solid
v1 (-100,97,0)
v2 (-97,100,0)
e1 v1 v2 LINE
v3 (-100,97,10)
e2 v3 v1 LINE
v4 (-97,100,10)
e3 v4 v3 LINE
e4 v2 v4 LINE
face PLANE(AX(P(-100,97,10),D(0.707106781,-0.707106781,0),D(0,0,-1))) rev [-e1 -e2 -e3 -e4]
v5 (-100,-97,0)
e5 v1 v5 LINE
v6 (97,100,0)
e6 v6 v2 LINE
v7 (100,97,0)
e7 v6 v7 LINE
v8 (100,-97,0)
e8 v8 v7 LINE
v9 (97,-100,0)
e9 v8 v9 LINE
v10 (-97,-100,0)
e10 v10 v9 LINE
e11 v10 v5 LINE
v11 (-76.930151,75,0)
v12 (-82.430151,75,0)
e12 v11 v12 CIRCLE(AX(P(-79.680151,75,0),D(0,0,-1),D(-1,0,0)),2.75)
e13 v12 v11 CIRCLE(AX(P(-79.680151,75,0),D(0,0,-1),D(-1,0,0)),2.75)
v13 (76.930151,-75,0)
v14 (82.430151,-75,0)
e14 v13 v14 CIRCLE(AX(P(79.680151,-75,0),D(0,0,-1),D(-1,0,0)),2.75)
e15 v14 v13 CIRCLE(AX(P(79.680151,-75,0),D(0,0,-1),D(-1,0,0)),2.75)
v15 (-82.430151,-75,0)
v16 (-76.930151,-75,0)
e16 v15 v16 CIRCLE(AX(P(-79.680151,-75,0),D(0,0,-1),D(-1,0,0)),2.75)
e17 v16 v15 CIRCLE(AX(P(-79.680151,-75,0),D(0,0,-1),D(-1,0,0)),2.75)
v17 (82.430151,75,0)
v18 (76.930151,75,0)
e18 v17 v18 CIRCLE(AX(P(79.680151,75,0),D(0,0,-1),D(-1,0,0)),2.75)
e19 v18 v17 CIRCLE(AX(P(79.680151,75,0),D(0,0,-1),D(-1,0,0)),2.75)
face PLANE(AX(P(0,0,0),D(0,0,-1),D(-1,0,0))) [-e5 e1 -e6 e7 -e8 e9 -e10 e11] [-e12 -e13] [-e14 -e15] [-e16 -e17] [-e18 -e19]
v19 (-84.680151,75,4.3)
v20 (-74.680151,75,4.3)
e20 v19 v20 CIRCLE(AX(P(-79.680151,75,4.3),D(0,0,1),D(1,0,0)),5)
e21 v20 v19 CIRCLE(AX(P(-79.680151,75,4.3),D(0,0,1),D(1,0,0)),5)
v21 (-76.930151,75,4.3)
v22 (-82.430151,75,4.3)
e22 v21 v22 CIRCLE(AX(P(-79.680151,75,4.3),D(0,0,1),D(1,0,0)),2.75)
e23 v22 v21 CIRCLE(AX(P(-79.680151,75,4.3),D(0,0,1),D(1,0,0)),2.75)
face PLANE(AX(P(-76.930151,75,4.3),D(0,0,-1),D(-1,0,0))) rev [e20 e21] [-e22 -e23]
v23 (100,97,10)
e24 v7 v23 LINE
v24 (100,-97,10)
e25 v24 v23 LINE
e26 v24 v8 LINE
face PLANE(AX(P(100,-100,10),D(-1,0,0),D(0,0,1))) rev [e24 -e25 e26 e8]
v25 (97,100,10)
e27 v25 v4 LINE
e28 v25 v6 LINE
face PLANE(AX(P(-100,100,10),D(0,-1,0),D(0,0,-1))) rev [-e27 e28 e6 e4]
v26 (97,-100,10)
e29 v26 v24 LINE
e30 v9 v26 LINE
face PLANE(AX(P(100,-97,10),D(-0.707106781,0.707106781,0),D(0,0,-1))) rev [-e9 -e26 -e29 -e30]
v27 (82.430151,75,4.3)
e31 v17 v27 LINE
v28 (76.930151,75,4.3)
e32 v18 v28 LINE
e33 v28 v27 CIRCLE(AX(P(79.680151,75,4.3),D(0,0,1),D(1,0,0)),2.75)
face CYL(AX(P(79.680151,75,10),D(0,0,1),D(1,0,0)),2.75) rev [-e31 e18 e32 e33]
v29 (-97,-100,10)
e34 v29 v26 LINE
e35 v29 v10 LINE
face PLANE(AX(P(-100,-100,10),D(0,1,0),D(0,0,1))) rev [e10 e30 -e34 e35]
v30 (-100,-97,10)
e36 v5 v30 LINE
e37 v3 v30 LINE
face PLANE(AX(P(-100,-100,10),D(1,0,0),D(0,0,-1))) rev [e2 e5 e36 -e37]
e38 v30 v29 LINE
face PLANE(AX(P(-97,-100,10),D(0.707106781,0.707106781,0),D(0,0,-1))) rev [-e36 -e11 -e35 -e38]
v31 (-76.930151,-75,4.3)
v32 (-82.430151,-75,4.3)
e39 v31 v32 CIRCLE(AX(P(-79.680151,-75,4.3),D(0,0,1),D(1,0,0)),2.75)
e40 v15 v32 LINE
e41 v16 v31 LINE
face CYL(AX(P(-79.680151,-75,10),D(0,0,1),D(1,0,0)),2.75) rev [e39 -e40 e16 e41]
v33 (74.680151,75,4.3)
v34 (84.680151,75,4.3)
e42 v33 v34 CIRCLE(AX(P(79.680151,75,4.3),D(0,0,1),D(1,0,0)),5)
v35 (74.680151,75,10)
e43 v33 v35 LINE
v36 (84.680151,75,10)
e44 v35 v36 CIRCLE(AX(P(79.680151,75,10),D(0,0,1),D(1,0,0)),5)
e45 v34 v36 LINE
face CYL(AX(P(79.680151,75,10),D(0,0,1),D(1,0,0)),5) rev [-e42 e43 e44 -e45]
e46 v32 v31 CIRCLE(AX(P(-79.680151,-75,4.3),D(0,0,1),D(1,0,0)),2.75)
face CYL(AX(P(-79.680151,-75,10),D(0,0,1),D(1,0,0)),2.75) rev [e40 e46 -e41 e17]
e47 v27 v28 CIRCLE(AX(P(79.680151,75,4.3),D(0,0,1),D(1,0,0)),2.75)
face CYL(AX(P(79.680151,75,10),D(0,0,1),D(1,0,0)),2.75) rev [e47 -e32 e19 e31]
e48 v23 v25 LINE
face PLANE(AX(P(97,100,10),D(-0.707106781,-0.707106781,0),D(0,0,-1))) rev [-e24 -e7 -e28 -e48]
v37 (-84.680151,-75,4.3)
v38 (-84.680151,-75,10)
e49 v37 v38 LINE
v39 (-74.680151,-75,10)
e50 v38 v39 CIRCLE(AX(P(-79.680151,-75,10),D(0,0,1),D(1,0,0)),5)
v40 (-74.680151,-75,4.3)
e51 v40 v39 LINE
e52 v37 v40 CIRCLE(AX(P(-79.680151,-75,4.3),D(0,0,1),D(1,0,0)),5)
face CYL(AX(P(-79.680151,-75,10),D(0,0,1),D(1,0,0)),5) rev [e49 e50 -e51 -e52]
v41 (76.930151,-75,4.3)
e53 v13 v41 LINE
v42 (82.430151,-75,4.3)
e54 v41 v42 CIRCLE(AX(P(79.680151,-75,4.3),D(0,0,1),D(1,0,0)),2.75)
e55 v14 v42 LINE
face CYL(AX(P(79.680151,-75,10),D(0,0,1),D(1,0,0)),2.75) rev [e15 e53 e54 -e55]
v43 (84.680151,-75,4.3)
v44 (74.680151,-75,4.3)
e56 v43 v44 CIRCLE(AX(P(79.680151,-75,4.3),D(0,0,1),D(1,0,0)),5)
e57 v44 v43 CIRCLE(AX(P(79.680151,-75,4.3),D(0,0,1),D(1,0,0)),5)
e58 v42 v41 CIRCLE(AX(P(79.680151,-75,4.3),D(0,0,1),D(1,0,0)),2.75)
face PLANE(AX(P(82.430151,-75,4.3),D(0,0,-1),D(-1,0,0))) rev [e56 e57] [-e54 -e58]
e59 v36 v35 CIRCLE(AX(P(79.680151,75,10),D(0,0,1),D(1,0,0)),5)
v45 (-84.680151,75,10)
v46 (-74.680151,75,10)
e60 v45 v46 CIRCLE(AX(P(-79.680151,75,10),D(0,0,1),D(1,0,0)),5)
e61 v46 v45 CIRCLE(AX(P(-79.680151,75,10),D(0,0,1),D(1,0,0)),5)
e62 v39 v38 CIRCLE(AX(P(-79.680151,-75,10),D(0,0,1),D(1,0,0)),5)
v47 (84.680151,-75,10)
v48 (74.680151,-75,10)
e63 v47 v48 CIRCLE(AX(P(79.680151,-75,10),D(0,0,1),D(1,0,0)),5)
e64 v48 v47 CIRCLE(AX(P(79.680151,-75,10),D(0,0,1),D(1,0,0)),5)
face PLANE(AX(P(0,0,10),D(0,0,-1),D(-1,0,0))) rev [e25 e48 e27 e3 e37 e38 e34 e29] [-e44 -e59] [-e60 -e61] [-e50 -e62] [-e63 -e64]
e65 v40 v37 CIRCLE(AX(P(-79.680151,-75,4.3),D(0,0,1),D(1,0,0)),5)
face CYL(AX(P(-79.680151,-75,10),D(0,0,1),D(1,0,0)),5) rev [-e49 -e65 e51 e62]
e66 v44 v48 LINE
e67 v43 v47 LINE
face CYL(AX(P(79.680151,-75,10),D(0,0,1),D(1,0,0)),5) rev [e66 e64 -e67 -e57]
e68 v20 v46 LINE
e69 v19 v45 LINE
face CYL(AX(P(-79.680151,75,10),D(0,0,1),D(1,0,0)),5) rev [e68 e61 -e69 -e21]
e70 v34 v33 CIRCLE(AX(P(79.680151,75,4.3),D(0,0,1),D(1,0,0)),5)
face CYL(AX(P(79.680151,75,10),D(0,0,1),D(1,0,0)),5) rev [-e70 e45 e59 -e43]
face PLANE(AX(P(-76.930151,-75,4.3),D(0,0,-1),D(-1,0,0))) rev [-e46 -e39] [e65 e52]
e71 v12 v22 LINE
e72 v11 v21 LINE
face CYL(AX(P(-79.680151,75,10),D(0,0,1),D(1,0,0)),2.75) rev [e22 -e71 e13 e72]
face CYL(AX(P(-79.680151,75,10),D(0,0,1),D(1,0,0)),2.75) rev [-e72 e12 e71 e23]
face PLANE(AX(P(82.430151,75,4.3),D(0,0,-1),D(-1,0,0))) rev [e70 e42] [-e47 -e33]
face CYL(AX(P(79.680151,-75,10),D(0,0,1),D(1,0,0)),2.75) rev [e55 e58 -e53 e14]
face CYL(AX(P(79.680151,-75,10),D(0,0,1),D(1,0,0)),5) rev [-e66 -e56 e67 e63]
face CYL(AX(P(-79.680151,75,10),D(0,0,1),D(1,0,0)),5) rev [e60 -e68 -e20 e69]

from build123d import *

# Parameters (mm, degrees)
SKETCH1_W                                            = 200
SKETCH1_H                                            = 200
BOSS_EXTRUDE1_DEPTH                                  = 10
CBORE_FOR_M5_HEXAGON_SOCKET_HEAD_CAP_SCR_D           = 5.5
CBORE_FOR_M5_HEXAGON_SOCKET_HEAD_CAP_SCR_DEPTH       = 36.9
CBORE_FOR_M5_HEXAGON_SOCKET_HEAD_CAP_SCR_CBORE_D     = 10
CBORE_FOR_M5_HEXAGON_SOCKET_HEAD_CAP_SCR_CBORE_DEPTH = 5.7
CBORE_FOR_M5_HEXAGON_SOCKET_HEAD_CAP_SCR_TIP         = 1.652366702
CHAMFER1_SIZE                                        = 3


with BuildPart() as part:
    # Sketch1 → Boss-Extrude1 (new body)
    with BuildSketch(Plane.XY):
        Rectangle(SKETCH1_W, SKETCH1_H)
    extrude(amount=BOSS_EXTRUDE1_DEPTH)

    # CBORE for M5 Hexagon socket head cap screws1
    with Locations(Plane.XY.offset(10)):
        with Locations((-79.680151025, 75), (79.680151025, 75), (79.680151025, -75), (-79.680151025, -75)):
            CounterBoreHole(CBORE_FOR_M5_HEXAGON_SOCKET_HEAD_CAP_SCR_D / 2, CBORE_FOR_M5_HEXAGON_SOCKET_HEAD_CAP_SCR_CBORE_D / 2, CBORE_FOR_M5_HEXAGON_SOCKET_HEAD_CAP_SCR_CBORE_DEPTH, depth=CBORE_FOR_M5_HEXAGON_SOCKET_HEAD_CAP_SCR_DEPTH)
            with Locations((0, 0, -(CBORE_FOR_M5_HEXAGON_SOCKET_HEAD_CAP_SCR_DEPTH + CBORE_FOR_M5_HEXAGON_SOCKET_HEAD_CAP_SCR_TIP / 2))):  # 118° drill point
                Cone(0, CBORE_FOR_M5_HEXAGON_SOCKET_HEAD_CAP_SCR_D / 2, CBORE_FOR_M5_HEXAGON_SOCKET_HEAD_CAP_SCR_TIP, mode=Mode.SUBTRACT)

    # Chamfer1
    chamfer1_edges = [part.edges().sort_by_distance(p)[0] for p in [
        (100, -100, 5),
        (-100, -100, 5),
        (-100, 100, 5),
        (100, 100, 5),
    ]]
    chamfer(chamfer1_edges, length=CHAMFER1_SIZE)


solid = part.part
